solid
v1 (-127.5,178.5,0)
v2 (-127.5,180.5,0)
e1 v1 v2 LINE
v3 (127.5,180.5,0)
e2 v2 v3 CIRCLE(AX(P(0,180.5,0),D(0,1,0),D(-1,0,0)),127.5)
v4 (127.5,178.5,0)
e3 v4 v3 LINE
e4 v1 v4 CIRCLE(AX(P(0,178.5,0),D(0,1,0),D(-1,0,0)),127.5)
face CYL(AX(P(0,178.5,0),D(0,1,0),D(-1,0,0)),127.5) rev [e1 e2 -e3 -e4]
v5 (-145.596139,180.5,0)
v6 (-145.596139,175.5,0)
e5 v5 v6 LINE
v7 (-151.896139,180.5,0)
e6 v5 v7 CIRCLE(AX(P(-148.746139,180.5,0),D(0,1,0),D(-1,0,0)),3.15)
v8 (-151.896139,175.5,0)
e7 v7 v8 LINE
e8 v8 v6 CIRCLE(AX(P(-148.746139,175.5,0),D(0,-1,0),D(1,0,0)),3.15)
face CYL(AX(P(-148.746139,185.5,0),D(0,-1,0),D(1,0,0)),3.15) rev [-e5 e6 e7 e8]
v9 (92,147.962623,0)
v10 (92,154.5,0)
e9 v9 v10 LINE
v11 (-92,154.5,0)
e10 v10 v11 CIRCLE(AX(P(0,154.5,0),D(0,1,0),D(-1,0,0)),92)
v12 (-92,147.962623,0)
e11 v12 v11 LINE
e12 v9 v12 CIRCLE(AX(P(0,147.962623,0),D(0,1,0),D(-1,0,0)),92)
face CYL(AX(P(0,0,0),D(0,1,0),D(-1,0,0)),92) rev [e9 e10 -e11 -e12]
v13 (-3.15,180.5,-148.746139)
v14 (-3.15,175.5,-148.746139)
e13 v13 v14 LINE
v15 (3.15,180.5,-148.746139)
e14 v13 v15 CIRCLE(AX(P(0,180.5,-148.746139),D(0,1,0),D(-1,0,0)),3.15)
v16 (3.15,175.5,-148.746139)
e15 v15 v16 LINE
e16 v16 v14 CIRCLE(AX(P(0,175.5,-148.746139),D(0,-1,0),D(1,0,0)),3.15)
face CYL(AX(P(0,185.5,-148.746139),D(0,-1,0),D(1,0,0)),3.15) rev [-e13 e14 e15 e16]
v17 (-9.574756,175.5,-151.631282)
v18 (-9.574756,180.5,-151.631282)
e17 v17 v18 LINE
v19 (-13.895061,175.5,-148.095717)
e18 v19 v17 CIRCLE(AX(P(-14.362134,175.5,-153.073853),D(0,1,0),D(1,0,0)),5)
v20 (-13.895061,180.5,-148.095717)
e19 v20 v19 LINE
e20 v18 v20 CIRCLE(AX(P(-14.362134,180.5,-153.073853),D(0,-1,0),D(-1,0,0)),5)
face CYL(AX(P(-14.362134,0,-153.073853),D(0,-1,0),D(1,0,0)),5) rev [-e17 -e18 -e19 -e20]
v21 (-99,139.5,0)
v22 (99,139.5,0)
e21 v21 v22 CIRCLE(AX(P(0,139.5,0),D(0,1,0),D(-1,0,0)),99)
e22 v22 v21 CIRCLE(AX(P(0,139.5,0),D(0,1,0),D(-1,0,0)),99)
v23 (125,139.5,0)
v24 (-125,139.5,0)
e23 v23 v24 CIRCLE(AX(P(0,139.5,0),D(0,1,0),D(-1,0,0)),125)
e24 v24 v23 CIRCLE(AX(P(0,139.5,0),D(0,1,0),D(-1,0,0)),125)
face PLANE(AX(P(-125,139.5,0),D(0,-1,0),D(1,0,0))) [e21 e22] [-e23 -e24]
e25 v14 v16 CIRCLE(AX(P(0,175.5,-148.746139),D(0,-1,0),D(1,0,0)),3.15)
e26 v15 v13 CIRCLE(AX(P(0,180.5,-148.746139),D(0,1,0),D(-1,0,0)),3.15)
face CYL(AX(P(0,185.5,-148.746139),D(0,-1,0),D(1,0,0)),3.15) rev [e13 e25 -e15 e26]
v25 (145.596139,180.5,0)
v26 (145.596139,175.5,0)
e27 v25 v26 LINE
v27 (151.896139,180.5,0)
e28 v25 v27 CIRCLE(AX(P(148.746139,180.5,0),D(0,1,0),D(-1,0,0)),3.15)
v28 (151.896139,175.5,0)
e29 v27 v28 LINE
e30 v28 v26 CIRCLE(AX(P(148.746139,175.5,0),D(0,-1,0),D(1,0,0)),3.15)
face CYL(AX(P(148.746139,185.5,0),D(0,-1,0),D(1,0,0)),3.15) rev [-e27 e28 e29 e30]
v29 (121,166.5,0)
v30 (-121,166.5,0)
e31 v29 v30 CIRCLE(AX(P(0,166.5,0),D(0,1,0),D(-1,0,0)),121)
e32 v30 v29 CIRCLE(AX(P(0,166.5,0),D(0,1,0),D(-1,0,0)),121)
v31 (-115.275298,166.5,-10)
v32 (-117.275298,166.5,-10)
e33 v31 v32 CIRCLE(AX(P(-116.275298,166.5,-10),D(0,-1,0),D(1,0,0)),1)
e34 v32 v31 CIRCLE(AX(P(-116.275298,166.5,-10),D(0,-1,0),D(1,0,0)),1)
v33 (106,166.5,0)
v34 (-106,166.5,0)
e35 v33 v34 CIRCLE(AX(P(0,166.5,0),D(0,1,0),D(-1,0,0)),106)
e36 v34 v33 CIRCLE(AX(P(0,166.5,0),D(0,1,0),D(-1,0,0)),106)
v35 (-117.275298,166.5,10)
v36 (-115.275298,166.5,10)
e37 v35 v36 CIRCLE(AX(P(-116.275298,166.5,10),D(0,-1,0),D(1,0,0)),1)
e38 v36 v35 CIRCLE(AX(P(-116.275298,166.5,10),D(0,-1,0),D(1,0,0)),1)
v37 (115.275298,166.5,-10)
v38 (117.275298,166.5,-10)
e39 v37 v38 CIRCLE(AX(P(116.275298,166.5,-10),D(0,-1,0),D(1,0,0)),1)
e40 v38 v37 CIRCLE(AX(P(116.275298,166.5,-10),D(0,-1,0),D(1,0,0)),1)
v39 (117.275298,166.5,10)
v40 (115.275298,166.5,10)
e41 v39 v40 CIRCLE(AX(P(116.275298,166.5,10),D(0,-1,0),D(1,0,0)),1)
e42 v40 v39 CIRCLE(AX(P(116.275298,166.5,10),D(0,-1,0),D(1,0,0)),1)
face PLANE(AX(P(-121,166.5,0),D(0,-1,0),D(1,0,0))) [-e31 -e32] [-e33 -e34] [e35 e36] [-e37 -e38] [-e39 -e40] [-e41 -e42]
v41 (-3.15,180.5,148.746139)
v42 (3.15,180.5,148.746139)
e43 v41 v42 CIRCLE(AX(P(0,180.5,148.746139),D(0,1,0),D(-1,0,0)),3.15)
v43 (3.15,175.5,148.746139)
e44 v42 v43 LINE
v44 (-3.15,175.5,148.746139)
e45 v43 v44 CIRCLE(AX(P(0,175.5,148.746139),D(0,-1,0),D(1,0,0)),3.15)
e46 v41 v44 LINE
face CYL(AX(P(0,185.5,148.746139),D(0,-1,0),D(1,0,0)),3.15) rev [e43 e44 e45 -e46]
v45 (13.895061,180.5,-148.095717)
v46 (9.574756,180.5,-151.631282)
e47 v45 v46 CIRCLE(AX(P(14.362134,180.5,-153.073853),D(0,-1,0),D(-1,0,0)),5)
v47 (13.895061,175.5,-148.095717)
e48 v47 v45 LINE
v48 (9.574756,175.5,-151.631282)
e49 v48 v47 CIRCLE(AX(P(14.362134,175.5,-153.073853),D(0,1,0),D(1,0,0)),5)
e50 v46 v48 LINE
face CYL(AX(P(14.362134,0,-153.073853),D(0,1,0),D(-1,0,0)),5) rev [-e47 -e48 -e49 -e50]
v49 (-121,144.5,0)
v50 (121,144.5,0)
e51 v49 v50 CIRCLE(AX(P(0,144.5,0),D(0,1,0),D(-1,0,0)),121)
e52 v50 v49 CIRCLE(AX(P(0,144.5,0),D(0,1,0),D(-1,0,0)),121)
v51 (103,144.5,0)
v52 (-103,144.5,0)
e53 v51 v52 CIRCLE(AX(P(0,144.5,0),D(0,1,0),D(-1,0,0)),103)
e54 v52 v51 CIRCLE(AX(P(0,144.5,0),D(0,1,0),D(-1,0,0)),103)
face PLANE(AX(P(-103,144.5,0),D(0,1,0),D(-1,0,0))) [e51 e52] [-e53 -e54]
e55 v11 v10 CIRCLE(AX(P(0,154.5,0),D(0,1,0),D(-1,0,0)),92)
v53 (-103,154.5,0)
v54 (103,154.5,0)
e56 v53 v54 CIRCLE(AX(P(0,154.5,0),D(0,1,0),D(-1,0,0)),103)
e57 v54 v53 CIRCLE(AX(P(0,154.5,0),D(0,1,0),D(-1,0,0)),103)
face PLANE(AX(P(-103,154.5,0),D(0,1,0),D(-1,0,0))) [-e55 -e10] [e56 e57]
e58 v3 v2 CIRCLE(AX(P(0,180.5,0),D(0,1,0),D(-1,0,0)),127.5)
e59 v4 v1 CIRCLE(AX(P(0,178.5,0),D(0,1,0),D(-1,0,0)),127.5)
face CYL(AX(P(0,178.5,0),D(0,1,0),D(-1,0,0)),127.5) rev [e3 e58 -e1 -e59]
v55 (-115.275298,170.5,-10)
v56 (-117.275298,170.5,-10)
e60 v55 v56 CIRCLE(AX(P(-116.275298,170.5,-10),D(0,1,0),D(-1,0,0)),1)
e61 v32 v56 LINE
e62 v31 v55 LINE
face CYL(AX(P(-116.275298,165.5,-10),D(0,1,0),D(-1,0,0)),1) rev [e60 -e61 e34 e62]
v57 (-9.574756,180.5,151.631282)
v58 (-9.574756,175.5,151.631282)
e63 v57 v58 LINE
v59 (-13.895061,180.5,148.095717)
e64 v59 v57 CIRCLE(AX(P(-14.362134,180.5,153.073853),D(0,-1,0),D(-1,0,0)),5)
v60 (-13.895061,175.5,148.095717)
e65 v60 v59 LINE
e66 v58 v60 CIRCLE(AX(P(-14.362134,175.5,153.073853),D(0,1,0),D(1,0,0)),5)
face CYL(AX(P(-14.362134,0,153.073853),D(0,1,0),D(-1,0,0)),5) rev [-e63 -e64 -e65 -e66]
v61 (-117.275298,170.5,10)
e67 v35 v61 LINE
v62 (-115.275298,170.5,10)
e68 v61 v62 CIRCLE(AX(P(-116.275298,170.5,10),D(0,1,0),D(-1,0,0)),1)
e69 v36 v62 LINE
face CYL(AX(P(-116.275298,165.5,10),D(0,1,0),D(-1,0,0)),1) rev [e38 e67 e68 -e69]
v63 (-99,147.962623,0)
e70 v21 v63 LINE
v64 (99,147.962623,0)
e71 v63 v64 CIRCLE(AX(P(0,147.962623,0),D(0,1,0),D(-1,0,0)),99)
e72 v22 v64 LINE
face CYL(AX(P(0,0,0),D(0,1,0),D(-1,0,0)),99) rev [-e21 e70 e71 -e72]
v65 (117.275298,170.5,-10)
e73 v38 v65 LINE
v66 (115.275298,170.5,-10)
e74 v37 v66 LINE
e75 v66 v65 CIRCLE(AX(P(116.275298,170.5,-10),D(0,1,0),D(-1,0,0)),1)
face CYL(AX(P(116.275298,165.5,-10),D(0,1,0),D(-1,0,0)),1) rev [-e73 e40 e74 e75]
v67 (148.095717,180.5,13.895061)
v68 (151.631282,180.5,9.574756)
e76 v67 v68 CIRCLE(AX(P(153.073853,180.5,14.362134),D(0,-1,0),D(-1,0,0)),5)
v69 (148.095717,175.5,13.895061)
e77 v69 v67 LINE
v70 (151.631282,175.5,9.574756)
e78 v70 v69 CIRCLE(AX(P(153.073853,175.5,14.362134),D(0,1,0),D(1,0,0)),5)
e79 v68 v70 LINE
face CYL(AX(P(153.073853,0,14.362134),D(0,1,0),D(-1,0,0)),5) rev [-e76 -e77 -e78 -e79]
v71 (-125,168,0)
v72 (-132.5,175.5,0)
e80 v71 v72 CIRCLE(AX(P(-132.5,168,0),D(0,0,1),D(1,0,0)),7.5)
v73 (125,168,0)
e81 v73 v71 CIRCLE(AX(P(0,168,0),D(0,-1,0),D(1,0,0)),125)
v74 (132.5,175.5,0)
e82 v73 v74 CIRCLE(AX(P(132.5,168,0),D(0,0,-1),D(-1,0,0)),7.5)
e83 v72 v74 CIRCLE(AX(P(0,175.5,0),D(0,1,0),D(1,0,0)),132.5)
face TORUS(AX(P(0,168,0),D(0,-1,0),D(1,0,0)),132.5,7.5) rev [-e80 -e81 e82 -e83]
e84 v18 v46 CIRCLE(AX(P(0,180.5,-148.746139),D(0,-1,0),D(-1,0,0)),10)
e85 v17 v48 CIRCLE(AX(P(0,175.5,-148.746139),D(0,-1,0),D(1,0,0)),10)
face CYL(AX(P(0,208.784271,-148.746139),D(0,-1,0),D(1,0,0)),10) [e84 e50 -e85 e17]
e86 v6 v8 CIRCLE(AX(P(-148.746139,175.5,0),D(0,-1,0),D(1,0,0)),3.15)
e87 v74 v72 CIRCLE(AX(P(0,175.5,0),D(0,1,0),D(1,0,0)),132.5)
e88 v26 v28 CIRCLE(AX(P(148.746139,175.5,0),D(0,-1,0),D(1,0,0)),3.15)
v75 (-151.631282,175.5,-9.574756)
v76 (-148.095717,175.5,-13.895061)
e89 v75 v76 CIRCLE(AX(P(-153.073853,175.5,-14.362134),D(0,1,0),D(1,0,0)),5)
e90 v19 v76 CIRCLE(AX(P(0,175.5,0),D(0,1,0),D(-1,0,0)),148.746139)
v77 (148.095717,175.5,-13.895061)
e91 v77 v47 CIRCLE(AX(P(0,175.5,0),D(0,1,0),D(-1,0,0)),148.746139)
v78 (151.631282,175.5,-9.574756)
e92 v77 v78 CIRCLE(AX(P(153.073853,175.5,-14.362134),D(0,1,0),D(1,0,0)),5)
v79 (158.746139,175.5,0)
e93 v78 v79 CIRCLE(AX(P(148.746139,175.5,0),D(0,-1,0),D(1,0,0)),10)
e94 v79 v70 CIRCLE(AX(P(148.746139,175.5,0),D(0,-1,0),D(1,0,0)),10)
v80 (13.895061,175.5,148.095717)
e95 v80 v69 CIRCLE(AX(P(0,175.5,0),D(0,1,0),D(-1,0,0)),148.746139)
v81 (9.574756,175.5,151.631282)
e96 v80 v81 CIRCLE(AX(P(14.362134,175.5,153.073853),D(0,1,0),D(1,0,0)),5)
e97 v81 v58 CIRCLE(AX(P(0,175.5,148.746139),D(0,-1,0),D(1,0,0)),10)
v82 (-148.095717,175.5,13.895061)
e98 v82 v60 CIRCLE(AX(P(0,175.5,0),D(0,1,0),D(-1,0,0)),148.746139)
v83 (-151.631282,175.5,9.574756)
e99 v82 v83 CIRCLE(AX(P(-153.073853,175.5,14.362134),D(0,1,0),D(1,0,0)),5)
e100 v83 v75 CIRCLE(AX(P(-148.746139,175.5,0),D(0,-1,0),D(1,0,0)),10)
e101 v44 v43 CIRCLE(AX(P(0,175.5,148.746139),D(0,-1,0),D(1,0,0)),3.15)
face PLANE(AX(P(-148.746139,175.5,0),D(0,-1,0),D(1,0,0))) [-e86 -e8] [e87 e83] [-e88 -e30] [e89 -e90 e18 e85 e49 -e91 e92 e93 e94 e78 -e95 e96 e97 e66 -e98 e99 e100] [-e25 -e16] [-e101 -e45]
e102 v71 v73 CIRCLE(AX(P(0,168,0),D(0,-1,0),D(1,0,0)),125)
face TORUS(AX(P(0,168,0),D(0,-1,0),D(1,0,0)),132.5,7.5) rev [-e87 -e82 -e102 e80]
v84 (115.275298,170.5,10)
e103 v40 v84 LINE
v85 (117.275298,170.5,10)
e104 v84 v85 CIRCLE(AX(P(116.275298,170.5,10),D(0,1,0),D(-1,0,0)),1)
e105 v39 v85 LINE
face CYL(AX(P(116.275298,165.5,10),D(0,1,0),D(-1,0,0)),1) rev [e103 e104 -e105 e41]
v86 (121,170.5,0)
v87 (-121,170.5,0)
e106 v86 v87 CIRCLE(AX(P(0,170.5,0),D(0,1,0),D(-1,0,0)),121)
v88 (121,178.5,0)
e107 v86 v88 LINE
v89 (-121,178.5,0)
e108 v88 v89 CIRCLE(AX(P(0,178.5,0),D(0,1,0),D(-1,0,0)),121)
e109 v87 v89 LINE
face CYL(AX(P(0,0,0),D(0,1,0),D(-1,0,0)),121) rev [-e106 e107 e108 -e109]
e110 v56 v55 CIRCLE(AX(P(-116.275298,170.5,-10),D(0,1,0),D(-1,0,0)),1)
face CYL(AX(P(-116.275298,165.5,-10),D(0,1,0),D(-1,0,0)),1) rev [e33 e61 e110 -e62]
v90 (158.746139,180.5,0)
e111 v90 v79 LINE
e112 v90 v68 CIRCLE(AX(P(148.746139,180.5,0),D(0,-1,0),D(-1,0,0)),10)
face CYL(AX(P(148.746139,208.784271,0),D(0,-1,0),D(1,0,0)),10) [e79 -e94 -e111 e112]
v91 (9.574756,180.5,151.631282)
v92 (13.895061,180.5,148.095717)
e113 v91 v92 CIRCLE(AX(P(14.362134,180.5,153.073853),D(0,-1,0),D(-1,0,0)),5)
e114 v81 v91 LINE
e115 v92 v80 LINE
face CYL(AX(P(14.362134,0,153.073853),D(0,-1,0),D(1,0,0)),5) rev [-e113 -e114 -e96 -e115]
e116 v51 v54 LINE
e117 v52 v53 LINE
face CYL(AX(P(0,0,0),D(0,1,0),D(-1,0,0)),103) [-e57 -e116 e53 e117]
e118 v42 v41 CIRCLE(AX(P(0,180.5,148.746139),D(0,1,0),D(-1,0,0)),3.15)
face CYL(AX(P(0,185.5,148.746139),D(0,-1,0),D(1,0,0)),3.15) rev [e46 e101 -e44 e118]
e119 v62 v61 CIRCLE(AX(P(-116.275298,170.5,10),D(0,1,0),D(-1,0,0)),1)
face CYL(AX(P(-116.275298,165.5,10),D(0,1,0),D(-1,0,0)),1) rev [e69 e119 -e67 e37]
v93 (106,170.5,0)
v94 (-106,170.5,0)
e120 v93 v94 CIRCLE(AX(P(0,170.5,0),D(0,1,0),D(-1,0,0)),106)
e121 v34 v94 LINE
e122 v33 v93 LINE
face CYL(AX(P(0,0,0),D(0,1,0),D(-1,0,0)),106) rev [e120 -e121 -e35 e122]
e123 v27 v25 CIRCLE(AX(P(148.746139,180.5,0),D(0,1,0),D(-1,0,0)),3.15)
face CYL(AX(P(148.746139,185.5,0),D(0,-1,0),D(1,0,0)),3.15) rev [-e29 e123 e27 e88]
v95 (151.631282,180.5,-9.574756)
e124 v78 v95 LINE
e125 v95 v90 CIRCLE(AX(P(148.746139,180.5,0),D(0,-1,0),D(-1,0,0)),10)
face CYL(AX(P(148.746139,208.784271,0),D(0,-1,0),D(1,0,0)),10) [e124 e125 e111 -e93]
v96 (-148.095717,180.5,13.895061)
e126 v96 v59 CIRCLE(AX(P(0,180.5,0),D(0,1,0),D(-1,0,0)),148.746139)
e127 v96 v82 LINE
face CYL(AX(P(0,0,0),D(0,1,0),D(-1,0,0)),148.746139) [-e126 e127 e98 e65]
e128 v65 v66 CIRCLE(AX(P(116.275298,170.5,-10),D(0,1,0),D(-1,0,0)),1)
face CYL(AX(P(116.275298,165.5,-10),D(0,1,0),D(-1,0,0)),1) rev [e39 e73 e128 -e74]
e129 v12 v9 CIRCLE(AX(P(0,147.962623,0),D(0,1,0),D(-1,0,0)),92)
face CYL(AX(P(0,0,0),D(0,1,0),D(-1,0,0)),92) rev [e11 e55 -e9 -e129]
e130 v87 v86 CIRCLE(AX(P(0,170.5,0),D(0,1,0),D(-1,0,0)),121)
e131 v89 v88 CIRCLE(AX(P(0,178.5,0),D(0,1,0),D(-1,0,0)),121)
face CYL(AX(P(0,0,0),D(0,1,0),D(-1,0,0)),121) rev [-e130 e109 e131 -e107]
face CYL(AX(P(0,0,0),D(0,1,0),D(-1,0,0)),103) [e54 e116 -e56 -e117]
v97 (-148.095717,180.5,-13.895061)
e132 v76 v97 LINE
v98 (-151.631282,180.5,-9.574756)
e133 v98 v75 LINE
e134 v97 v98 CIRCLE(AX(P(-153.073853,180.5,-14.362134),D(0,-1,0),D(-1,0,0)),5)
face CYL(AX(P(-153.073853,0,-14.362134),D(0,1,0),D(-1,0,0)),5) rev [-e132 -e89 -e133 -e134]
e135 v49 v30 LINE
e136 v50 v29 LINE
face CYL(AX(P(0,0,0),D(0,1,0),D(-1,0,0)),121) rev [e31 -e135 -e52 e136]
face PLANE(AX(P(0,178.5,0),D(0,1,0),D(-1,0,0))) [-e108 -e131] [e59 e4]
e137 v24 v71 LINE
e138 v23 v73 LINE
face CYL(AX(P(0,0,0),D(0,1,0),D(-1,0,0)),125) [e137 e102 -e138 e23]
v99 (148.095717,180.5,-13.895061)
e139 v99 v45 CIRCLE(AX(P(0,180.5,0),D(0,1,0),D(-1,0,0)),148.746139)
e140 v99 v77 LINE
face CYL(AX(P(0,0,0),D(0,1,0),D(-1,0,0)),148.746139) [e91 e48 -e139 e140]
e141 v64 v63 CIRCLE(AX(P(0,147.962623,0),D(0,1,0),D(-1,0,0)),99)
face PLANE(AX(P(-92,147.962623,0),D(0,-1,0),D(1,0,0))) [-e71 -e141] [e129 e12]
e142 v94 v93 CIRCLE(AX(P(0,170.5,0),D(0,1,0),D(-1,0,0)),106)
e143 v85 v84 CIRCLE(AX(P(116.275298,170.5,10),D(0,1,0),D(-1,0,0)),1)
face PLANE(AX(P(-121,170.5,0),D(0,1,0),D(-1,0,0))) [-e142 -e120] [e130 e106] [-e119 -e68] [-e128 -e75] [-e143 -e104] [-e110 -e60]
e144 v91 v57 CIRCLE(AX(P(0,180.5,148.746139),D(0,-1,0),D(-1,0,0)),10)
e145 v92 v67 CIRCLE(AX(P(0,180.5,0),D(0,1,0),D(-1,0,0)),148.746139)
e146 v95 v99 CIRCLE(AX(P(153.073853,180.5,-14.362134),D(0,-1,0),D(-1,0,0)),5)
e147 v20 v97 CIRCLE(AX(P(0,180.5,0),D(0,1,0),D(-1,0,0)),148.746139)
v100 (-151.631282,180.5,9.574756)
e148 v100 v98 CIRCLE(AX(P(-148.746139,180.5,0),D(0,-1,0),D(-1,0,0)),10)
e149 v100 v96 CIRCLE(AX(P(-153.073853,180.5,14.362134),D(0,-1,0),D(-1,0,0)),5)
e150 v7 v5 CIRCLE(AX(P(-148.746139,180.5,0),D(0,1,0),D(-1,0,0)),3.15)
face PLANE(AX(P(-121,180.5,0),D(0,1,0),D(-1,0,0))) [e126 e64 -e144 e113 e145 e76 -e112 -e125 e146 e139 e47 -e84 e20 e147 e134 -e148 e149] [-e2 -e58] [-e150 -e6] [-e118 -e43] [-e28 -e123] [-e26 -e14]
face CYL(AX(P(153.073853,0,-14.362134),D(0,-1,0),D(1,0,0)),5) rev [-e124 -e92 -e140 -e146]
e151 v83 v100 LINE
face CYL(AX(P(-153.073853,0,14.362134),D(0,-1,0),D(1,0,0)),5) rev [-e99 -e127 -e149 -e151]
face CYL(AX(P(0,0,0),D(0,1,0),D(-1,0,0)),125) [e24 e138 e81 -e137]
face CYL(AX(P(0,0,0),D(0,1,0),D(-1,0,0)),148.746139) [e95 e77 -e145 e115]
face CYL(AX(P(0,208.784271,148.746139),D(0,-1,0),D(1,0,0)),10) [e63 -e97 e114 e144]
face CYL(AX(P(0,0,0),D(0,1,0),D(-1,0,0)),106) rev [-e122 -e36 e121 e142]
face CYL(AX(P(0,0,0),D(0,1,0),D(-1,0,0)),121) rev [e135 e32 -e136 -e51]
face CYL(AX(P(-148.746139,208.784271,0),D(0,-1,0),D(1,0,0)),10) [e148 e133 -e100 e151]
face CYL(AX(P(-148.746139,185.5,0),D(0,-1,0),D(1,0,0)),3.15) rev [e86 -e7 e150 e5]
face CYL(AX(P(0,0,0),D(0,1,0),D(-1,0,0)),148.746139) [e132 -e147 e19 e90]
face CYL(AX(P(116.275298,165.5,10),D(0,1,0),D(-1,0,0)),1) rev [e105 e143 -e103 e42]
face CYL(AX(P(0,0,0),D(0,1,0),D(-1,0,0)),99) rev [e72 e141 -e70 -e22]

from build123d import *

# Parameters (mm, degrees)
SKETCH2_R           = 127.5
CUT_EXTRUDE1_DEPTH  = 2
SKETCH3_R           = 10
BOSS_EXTRUDE1_DEPTH = 5
FILLET1_R           = 5
SKETCH4_R           = 3.15
CUT_EXTRUDE2_DEPTH  = 10
FILLET2_R           = 7.5
SKETCH5_R           = 1
CUT_EXTRUDE3_DEPTH  = 5


with BuildPart() as part:
    # Sketch1 → Revolve1 (revolve)
    with BuildSketch(Plane.XY):
        Polygon((-125, 139.5), (-125, 175.5), (-148.746139417, 175.5), (-148.746139417, 180.5), (-121, 180.5), (-121, 170.5), (-106, 170.5), (-106, 166.5), (-121, 166.5), (-121, 144.5), (-103, 144.5), (-103, 154.5), (-92, 154.5), (-92, 147.962623379), (-99, 147.962623379), (-99, 139.5), align=None)
    revolve(axis=Axis((0, 0, 0), (0, -1, 0)))

    # Sketch2 → Cut-Extrude1 (cut)
    with BuildSketch(Plane(origin=(0, 180.5, 0), x_dir=(1, 0, 0), z_dir=(0, 1, 0))):
        with Locations(Location((0, 0, 0), (0, 0, 180))):
            Circle(SKETCH2_R)
    extrude(amount=-CUT_EXTRUDE1_DEPTH, mode=Mode.SUBTRACT)

    # Sketch3 → Boss-Extrude1 (add)
    with BuildSketch(Plane.XZ.offset(-175.5)):
        with Locations((0, -148.746139417)):
            Circle(SKETCH3_R)
        with Locations((-148.746139417, 0)):
            Circle(SKETCH3_R)
        with Locations((0, 148.746139417)):
            Circle(SKETCH3_R)
        with Locations((148.746139417, 0)):
            Circle(SKETCH3_R)
    extrude(amount=-BOSS_EXTRUDE1_DEPTH)

    # Fillet1
    fillet1_edges = [part.edges().sort_by_distance(p)[0] for p in [
        (-9.994348791, 178, -148.409996239),
        (9.994348791, 178, -148.409996239),
        (-148.409996239, 178, 9.994348791),
        (-148.409996239, 178, -9.994348791),
        (9.994348791, 178, 148.409996239),
        (-9.994348791, 178, 148.409996239),
        (148.409996239, 178, -9.994348791),
        (148.409996239, 178, 9.994348791),
    ]]
    fillet(fillet1_edges, radius=FILLET1_R)

    # Sketch4 → Cut-Extrude2 (cut)
    with BuildSketch(Plane.XZ.offset(-175.5)):
        with Locations((148.746139417, 0)):
            Circle(SKETCH4_R)
        with Locations((0, -148.746139417)):
            Circle(SKETCH4_R)
        with Locations((-148.746139417, 0)):
            Circle(SKETCH4_R)
        with Locations((0, 148.746139417)):
            Circle(SKETCH4_R)
    extrude(amount=-CUT_EXTRUDE2_DEPTH, mode=Mode.SUBTRACT)

    # Fillet2
    fillet2_edges = [part.edges().sort_by_distance(p)[0] for p in [
        (125, 175.5, 0),
    ]]
    fillet(fillet2_edges, radius=FILLET2_R)

    # Sketch5 → Cut-Extrude3 (cut)
    with BuildSketch(Plane(origin=(0, 170.5, 0), x_dir=(1, 0, 0), z_dir=(0, 1, 0))):
        with Locations(Location((-116.275298476, 10, 0), (0, 0, 180))):
            Circle(SKETCH5_R)
        with Locations(Location((-116.275298476, -10, 0), (0, 0, 180))):
            Circle(SKETCH5_R)
        with Locations(Location((116.275298476, 10, 0), (0, 0, 180))):
            Circle(SKETCH5_R)
        with Locations(Location((116.275298476, -10, 0), (0, 0, 180))):
            Circle(SKETCH5_R)
    extrude(amount=-CUT_EXTRUDE3_DEPTH, mode=Mode.SUBTRACT)


solid = part.part
